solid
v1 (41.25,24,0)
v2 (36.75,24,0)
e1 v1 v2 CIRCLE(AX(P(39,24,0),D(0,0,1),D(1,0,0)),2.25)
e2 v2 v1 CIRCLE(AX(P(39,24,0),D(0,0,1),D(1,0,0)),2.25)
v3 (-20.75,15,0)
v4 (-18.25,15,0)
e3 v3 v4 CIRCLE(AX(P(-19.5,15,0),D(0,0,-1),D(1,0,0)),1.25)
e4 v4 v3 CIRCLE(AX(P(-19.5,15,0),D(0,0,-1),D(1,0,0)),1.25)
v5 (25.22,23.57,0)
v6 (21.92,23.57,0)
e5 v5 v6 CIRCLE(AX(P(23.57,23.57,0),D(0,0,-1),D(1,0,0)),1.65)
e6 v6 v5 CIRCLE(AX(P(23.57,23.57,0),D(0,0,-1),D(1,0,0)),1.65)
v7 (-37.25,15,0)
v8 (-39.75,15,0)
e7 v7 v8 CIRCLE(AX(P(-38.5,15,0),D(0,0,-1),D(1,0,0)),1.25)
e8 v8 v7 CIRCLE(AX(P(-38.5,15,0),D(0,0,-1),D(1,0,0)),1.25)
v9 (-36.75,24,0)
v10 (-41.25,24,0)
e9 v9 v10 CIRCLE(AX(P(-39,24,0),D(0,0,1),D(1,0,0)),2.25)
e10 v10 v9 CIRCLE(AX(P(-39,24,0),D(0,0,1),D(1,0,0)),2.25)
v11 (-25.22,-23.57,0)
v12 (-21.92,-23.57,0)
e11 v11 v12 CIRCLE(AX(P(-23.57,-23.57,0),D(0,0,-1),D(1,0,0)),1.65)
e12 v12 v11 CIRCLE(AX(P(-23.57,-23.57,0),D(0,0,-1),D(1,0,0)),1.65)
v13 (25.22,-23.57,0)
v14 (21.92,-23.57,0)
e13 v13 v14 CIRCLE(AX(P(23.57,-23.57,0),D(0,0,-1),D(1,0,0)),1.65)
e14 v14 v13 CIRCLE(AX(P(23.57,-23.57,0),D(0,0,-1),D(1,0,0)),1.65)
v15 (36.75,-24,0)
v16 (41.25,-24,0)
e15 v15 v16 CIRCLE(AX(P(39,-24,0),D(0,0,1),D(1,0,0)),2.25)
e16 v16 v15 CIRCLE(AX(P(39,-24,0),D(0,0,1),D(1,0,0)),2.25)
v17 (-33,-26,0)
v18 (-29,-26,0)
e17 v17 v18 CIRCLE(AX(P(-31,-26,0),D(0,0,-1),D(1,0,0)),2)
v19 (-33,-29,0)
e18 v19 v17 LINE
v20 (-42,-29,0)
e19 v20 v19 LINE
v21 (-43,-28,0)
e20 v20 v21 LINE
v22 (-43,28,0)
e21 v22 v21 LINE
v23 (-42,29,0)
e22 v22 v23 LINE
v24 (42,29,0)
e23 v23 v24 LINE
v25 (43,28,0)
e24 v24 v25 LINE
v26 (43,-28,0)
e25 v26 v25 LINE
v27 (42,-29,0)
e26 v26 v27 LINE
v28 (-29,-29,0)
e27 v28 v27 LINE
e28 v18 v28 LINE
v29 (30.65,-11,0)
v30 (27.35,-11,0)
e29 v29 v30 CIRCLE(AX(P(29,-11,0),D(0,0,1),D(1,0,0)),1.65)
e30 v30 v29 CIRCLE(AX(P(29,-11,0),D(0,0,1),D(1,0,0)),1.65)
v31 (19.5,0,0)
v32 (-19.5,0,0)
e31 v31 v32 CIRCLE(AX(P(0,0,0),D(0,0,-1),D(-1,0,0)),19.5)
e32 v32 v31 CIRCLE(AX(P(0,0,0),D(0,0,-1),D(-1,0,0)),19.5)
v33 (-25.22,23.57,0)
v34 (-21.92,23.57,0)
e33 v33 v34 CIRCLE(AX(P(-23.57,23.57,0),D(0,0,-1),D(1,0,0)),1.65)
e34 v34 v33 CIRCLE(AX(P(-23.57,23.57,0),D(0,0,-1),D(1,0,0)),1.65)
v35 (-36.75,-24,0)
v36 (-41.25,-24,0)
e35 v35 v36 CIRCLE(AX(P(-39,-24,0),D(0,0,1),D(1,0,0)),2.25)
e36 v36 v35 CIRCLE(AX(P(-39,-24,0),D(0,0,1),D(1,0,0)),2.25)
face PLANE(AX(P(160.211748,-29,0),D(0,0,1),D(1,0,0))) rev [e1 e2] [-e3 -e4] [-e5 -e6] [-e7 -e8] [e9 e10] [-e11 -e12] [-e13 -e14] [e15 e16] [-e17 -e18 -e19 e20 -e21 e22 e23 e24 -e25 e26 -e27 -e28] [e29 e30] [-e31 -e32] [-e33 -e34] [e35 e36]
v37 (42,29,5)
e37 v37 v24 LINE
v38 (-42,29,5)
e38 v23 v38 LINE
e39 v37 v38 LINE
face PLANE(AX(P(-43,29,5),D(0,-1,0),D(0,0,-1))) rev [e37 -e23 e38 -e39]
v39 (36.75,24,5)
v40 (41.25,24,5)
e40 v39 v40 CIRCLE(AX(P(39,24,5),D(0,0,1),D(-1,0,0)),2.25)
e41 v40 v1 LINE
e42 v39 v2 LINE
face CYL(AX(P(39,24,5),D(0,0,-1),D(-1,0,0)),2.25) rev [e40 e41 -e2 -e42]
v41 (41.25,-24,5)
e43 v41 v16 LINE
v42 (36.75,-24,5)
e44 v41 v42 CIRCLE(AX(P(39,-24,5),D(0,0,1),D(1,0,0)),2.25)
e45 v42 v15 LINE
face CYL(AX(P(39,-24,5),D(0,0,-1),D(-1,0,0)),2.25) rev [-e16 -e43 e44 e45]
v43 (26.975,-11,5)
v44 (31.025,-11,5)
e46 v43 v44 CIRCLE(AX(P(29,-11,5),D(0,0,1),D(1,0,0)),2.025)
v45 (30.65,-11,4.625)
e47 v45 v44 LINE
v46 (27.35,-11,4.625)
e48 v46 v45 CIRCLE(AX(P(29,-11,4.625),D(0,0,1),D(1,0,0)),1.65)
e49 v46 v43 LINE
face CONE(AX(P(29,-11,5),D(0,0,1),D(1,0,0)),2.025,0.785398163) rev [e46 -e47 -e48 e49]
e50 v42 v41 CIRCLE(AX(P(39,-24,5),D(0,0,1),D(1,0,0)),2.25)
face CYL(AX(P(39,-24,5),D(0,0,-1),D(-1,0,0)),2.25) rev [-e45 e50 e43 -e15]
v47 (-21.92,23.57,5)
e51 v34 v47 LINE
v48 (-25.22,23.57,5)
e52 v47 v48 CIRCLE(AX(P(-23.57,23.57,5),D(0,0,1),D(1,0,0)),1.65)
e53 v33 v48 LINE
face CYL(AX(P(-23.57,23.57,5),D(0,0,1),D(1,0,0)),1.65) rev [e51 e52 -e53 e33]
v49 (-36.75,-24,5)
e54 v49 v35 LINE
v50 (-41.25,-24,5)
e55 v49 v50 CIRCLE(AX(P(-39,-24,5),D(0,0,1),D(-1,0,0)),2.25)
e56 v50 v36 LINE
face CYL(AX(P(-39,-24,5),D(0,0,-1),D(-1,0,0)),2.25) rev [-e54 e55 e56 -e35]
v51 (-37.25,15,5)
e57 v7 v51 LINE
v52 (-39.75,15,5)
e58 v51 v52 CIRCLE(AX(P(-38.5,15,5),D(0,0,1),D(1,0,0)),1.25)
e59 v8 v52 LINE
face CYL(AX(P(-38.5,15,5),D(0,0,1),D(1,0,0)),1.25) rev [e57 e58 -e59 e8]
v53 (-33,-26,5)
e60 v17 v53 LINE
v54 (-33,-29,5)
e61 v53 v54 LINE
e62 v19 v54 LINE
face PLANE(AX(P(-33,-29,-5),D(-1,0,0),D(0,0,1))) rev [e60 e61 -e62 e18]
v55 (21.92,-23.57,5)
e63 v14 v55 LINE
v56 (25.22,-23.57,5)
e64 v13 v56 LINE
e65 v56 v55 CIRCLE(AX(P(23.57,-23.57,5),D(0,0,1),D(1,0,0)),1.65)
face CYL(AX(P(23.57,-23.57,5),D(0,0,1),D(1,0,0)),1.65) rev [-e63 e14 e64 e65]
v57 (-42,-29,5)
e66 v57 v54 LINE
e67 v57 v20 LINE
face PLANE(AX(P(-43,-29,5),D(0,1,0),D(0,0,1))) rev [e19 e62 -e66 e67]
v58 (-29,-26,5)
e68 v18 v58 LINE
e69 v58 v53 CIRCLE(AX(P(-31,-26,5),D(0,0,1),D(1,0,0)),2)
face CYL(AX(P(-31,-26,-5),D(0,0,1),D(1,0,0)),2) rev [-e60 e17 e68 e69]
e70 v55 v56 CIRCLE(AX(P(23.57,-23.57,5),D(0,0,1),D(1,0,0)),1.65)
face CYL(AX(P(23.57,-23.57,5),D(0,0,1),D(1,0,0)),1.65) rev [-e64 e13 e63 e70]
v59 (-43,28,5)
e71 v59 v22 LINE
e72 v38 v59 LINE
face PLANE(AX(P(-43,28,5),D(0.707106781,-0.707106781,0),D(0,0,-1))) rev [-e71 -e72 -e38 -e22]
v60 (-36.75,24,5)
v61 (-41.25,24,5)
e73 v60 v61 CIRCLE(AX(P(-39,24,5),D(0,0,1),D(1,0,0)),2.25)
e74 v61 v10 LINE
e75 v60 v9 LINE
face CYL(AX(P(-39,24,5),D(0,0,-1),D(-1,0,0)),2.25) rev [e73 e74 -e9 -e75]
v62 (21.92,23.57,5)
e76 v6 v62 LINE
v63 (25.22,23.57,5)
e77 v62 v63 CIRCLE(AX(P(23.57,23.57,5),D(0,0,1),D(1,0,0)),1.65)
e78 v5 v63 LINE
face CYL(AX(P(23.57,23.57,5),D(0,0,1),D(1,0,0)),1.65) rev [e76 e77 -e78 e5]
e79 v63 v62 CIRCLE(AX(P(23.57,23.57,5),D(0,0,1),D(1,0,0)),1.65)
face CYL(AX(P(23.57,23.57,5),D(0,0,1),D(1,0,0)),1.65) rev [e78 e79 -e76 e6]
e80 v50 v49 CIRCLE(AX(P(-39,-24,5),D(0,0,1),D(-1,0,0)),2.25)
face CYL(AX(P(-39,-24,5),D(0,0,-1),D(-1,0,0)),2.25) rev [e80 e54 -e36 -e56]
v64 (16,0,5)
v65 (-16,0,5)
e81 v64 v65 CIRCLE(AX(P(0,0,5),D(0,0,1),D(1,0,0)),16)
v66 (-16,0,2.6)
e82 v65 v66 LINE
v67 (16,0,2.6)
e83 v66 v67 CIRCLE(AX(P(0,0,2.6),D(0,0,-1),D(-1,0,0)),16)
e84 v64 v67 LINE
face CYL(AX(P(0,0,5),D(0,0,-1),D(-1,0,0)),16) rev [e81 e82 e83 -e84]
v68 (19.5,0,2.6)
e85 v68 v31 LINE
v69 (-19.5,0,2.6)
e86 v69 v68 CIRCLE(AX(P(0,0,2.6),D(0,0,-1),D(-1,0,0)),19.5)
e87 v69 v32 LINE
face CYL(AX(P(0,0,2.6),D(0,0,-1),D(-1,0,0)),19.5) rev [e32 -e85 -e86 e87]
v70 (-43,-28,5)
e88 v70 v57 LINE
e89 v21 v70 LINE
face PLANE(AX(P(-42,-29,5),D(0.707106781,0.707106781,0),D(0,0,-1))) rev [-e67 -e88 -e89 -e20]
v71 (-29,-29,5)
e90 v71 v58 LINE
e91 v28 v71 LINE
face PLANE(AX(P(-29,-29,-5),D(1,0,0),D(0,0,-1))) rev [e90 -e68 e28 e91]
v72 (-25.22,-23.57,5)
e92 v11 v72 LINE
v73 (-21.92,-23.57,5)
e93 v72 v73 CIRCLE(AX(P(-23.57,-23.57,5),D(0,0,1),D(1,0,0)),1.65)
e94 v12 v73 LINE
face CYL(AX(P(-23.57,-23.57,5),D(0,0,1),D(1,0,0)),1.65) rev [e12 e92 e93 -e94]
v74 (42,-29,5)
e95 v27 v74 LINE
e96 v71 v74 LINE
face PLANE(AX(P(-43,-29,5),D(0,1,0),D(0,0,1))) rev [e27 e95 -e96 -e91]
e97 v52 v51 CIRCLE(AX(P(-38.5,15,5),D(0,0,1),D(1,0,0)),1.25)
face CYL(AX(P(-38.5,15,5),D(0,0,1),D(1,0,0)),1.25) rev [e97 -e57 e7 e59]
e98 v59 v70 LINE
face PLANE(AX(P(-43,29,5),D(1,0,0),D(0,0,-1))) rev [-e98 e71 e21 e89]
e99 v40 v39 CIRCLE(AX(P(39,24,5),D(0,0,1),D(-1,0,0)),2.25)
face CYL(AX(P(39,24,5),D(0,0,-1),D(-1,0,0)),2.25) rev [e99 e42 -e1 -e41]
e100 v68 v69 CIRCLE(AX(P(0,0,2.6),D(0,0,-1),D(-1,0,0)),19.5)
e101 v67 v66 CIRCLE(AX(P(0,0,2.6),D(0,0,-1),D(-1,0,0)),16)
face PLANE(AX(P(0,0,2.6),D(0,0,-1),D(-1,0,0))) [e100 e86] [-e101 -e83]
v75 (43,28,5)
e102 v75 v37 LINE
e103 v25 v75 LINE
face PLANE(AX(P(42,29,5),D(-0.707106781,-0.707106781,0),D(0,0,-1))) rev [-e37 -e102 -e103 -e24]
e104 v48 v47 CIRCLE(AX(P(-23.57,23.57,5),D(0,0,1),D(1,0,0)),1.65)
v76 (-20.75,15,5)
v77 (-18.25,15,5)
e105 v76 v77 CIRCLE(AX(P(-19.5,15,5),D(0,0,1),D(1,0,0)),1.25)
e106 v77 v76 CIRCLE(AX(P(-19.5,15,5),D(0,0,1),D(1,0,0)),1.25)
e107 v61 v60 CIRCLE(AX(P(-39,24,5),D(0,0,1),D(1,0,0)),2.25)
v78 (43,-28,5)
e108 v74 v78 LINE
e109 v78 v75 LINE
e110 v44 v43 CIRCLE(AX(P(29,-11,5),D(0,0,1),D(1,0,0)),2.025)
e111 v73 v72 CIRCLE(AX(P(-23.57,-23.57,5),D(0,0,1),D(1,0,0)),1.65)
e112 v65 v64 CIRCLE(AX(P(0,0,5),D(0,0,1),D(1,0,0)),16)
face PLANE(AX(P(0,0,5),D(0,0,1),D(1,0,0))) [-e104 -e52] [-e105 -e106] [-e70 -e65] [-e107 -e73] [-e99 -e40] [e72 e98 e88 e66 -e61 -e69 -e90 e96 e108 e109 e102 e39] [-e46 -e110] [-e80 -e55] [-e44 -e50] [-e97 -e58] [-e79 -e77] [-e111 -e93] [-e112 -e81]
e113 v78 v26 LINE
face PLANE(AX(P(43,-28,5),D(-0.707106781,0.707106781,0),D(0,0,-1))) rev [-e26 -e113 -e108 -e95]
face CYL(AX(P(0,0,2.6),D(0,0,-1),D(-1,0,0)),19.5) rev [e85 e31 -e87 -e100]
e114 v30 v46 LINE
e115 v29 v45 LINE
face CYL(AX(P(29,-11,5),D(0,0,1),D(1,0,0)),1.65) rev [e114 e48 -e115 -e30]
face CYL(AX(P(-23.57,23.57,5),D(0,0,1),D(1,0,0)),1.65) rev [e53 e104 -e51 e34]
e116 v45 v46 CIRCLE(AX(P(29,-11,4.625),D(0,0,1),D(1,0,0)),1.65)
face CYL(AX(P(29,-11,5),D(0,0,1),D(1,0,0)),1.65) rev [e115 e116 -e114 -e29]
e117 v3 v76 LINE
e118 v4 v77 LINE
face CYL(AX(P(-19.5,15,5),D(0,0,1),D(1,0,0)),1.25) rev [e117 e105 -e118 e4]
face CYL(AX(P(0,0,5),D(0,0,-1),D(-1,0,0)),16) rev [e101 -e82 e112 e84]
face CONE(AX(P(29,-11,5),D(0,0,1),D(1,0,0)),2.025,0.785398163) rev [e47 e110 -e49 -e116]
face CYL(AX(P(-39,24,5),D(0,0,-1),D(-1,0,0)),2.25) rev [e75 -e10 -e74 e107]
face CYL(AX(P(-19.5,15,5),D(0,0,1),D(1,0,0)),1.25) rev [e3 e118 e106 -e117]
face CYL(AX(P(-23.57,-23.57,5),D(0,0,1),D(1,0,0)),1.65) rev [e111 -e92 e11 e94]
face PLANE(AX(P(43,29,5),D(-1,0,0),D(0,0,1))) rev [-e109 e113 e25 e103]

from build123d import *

# Parameters (mm, degrees)
SKETCH_1_W                   = 86
SKETCH_1_H                   = 58
SKETCH_1_R                   = 16
SKETCH_1_R_2                 = 2.25
EXTRUDE_1_DEPTH              = 5
HOLE_WIZARD_M3_1_D           = 2.5
HOLE_WIZARD_M4_1_D           = 3.3
MIRROR_2_COPY_1_D            = 3.3
CUT_EXTRUDE_1_DEPTH          = 53.820450585
CHAMFER_1_SIZE               = 1
SKETCH_10_W                  = 216.550460162
SKETCH_10_H                  = 17.046792279
CUT_EXTRUDE_4_DEPTH          = 73.374028491
SKETCH_11_R                  = 19.5
CUT_EXTRUDE_5_DEPTH          = 2.6
SKETCH_13_R                  = 1.350406535
CUT_EXTRUDE_6_DEPTH          = 10
HOLE_WIZARD_M4_3_D           = 3.3
HOLE_WIZARD_M4_3_DEPTH       = 11.5
HOLE_WIZARD_M4_3_CSINK_D     = 4.05
HOLE_WIZARD_M4_3_CSINK_ANGLE = 90
HOLE_WIZARD_M4_3_TIP         = 0.991420021


with BuildPart() as part:
    # 草图1 → 凸台-拉伸1 (new, symmetric)
    with BuildSketch(Plane.XY):
        Rectangle(SKETCH_1_W, SKETCH_1_H)
        Circle(SKETCH_1_R, mode=Mode.SUBTRACT)
        with Locations((-39, 24)):
            Circle(SKETCH_1_R_2, mode=Mode.SUBTRACT)
        with Locations(Location((39, 24, 0), (0, 0, 180))):
            Circle(SKETCH_1_R_2, mode=Mode.SUBTRACT)
        with Locations((39, -24)):
            Circle(SKETCH_1_R_2, mode=Mode.SUBTRACT)
        with Locations(Location((-39, -24, 0), (0, 0, 180))):
            Circle(SKETCH_1_R_2, mode=Mode.SUBTRACT)
    extrude(amount=EXTRUDE_1_DEPTH, both=True)

    # M3 螺纹孔1 (through all)
    with Locations(Plane.XY.offset(5)):
        with Locations((-38.5, 15), (-19.5, 15)):
            Hole(HOLE_WIZARD_M3_1_D / 2)

    # M4 螺纹孔1 (through all)
    with Locations(Plane.XY.offset(5)):
        with Locations((-23.57, 23.57)):
            hole_wizard_m4_1 = Hole(HOLE_WIZARD_M4_1_D / 2)

    # 镜向1: M4 螺纹孔1 across plane
    add(hole_wizard_m4_1.mirror(Plane.ZX), mode=Mode.SUBTRACT)

    # 镜向2: M4 螺纹孔1 across plane
    add(hole_wizard_m4_1.mirror(Plane(origin=(0, 0, 0), x_dir=(0, 0, 1), z_dir=(1, 0, 0))), mode=Mode.SUBTRACT)

    # 镜向2 copy 1 (through all)
    with Locations(Plane(origin=(0, 0, 5), x_dir=(-1, 0, 0), z_dir=(0, 0, 1))):
        with Locations((-23.57, 23.57)):
            Hole(MIRROR_2_COPY_1_D / 2)

    # 草图7 → 切除-拉伸1 (cut, through all)
    with BuildSketch(Plane.XY.offset(5)):
        with BuildLine():
            Line((-33, -29), (-33, -26))
            ThreePointArc((-33, -26), (-31, -24), (-29, -26))
            Line((-29, -26), (-29, -29))
            ThreePointArc((-29, -29), (-31, -31), (-33, -29))
        make_face()
    extrude(amount=-CUT_EXTRUDE_1_DEPTH, mode=Mode.SUBTRACT)

    # 倒角1
    chamfer_1_edges = [part.edges().sort_by_distance(p)[0] for p in [
        (43, -29, 0),
        (-43, -29, 0),
        (-43, 29, 0),
        (43, 29, 0),
    ]]
    chamfer(chamfer_1_edges, length=CHAMFER_1_SIZE)

    # 草图10 → 切除-拉伸4 (cut, through all)
    with BuildSketch(Plane(origin=(0, 29, 0), x_dir=(1, 0, 0), z_dir=(0, 1, 0))):
        with Locations((51.936518235, 8.52339614)):
            Rectangle(SKETCH_10_W, SKETCH_10_H)
    extrude(amount=-CUT_EXTRUDE_4_DEPTH, mode=Mode.SUBTRACT)

    # 草图11 → 切除-拉伸5 (cut)
    with BuildSketch(Plane(origin=(0, 0, 0), x_dir=(-1, 0, 0), z_dir=(0, 0, -1))):
        Circle(SKETCH_11_R)
    extrude(amount=-CUT_EXTRUDE_5_DEPTH, mode=Mode.SUBTRACT)

    # 草图13 → 切除-拉伸6 (cut)
    with BuildSketch(Plane.XY.offset(5)):
        with Locations((29, -11)):
            Circle(SKETCH_13_R)
    extrude(amount=-CUT_EXTRUDE_6_DEPTH, mode=Mode.SUBTRACT)

    # M4 螺纹孔3
    with Locations(Plane(origin=(29, -11, 5), x_dir=(1, 0, 0), z_dir=(0, 0, 1))):
        with Locations((0, 0)):
            CounterSinkHole(HOLE_WIZARD_M4_3_D / 2, HOLE_WIZARD_M4_3_CSINK_D / 2, depth=HOLE_WIZARD_M4_3_DEPTH, counter_sink_angle=HOLE_WIZARD_M4_3_CSINK_ANGLE)
            with Locations((0, 0, -(HOLE_WIZARD_M4_3_DEPTH + HOLE_WIZARD_M4_3_TIP / 2))):  # 118° drill point
                Cone(0, HOLE_WIZARD_M4_3_D / 2, HOLE_WIZARD_M4_3_TIP, mode=Mode.SUBTRACT)


solid = part.part
